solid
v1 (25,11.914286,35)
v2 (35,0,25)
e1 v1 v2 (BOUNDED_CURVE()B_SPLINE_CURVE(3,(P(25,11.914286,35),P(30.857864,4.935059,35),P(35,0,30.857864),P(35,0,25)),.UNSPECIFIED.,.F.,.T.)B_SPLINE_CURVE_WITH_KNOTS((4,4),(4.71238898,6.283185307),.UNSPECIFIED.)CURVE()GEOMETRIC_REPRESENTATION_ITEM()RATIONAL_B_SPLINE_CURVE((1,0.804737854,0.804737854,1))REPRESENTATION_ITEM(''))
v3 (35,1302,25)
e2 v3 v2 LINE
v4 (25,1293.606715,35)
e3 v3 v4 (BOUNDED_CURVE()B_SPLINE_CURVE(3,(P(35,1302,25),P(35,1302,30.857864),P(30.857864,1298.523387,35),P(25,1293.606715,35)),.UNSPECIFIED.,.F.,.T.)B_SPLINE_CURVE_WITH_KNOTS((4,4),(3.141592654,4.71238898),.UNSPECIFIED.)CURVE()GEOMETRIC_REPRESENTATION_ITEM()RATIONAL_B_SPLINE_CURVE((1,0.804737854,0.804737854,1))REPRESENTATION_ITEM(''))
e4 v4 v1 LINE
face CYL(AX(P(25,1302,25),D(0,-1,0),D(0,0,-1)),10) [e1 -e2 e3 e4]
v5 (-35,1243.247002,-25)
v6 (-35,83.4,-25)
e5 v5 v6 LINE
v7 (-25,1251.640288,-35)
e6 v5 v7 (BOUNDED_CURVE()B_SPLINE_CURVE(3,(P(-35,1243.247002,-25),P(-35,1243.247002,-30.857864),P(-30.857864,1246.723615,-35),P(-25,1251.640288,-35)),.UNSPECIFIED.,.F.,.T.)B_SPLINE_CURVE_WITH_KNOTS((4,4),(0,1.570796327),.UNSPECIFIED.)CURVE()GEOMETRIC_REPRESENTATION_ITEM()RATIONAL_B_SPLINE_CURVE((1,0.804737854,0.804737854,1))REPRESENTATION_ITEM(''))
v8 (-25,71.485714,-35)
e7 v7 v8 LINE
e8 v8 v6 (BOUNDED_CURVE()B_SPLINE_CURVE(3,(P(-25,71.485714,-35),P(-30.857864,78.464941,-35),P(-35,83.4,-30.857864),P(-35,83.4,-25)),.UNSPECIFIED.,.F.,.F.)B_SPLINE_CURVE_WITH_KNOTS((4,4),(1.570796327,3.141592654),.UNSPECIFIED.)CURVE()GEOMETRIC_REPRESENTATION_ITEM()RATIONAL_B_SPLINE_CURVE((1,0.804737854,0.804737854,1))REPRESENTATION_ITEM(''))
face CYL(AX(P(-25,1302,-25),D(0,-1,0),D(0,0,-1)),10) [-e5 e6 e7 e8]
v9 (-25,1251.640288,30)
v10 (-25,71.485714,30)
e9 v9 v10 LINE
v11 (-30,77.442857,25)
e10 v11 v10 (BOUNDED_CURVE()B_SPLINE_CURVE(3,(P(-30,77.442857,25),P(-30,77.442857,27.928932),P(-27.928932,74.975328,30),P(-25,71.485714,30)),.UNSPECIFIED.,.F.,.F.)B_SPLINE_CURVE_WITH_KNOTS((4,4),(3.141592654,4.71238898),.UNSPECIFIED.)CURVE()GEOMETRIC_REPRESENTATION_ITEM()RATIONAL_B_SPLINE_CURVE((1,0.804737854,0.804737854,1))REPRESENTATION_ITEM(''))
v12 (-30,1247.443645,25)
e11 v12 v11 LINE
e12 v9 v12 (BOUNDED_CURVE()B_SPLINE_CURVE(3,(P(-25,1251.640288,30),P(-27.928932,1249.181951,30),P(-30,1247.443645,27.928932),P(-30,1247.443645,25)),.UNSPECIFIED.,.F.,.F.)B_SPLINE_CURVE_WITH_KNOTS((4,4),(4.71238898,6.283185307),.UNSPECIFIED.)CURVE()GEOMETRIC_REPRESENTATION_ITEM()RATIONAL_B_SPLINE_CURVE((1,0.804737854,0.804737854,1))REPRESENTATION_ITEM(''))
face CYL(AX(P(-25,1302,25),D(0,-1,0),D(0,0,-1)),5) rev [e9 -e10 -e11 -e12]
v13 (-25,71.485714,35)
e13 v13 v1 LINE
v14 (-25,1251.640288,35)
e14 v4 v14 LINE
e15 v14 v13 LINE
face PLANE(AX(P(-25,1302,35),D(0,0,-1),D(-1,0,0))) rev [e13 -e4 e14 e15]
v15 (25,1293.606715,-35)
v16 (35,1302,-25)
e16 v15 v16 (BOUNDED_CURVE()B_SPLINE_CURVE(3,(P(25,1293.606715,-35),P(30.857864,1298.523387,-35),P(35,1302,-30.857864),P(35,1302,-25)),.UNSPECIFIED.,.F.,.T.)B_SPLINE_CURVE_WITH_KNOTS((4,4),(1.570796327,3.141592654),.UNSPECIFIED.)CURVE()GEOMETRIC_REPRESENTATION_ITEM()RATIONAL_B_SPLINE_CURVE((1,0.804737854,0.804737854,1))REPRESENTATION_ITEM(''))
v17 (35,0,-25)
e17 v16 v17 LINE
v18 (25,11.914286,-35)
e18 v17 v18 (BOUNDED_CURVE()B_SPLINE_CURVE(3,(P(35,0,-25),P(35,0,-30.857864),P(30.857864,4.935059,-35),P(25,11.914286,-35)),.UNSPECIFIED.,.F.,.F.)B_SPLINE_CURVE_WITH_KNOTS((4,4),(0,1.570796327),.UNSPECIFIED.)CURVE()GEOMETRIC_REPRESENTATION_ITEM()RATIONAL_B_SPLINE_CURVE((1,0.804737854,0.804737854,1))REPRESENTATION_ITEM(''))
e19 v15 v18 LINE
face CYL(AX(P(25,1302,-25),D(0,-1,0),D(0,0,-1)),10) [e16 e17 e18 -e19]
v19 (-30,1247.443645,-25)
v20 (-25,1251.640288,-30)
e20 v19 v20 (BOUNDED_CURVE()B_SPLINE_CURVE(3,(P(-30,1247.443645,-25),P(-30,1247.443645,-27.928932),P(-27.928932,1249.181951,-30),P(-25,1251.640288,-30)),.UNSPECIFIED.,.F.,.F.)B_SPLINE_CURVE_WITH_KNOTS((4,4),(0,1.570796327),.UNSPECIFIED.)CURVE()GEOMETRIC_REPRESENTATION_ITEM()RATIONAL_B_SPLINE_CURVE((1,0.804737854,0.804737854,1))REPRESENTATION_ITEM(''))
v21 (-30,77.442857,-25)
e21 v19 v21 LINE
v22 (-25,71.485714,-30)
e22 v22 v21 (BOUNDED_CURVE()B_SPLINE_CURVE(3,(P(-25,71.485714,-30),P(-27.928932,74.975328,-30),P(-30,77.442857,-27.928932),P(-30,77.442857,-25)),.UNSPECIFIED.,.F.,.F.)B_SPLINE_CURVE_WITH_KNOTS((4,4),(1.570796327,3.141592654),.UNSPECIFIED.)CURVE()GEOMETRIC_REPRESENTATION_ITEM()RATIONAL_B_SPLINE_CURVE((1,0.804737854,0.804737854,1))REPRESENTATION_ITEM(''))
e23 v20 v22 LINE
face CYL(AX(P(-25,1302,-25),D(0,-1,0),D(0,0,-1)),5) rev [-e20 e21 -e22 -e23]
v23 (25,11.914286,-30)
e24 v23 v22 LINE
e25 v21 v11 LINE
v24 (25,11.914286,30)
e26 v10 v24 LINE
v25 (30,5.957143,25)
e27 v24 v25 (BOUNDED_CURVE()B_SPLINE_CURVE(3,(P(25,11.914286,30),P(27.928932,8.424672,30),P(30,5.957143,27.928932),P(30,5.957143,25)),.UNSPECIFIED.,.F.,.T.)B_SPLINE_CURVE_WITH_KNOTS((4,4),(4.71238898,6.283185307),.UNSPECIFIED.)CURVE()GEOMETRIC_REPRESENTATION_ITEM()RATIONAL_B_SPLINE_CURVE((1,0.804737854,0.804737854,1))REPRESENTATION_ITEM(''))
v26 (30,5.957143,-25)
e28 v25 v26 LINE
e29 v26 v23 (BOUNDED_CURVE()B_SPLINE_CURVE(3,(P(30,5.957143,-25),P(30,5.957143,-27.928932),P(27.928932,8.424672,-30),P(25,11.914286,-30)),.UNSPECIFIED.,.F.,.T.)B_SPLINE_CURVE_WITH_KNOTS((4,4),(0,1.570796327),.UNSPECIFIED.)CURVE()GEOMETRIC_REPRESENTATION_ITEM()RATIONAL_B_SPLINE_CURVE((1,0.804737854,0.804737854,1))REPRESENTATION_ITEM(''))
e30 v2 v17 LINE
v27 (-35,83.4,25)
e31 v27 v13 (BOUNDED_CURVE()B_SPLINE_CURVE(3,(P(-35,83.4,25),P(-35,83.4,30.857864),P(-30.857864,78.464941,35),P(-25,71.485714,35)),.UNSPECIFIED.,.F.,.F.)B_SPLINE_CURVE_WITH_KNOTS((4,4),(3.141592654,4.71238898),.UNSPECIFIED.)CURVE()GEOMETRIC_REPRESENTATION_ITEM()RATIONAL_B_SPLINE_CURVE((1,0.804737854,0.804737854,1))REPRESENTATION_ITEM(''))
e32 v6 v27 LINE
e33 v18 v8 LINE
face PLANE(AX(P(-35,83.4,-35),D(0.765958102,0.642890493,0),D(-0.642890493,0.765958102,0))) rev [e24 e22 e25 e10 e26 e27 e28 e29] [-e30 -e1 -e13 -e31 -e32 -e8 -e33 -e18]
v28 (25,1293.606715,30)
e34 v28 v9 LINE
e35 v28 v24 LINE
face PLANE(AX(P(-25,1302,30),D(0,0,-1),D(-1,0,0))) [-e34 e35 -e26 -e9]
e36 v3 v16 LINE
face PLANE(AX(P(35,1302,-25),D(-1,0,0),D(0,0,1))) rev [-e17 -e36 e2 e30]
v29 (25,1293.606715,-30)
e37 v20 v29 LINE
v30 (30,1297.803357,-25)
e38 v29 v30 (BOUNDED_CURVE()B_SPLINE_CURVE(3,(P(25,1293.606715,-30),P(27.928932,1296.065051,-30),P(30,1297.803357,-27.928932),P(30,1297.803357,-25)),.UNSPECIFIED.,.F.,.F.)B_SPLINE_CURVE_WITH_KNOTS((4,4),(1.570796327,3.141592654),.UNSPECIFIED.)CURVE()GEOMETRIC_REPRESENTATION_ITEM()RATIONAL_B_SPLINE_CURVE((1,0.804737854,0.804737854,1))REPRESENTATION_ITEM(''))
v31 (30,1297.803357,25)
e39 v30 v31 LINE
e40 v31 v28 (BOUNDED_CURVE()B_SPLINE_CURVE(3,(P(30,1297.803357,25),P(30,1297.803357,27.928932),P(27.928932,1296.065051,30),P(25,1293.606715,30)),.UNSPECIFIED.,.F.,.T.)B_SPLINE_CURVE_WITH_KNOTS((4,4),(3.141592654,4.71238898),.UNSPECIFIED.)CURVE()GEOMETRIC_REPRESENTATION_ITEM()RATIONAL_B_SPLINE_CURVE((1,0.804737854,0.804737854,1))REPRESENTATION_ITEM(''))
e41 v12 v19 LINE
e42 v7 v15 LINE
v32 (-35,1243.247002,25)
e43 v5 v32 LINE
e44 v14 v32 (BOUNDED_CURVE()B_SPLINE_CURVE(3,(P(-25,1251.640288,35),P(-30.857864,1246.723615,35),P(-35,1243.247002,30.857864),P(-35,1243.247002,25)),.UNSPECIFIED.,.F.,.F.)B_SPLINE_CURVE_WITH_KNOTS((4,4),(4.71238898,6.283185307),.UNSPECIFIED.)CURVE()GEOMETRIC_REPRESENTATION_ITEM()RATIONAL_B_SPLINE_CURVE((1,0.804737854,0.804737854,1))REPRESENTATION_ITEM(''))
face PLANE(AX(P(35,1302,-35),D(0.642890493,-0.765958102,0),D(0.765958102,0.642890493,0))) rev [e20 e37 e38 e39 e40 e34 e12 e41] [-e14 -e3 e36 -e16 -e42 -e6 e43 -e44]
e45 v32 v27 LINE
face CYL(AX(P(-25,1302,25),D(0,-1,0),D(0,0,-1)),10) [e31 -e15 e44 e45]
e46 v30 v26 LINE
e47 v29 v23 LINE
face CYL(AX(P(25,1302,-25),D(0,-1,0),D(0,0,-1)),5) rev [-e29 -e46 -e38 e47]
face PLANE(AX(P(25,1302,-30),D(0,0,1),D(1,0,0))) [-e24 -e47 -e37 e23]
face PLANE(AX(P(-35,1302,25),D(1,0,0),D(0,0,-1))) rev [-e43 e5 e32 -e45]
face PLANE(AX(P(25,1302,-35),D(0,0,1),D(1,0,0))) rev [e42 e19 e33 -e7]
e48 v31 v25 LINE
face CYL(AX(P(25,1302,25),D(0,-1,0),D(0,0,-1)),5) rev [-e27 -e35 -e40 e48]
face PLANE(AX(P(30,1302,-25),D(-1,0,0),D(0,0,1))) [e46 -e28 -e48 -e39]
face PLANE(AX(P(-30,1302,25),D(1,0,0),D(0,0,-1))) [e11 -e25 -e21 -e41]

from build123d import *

# Parameters (mm, degrees)
F_19_WELDMEMBERFEAT_4_MORE_IN_5_FILES_DEPTH = 1302
CUT_EXTRUDE1_DEPTH                          = 1305.350029708
CUT_EXTRUDE1_DEPTH_BACK                     = 1305.350029708


with BuildPart() as part:
    # Sketch1 → 19 (WeldMemberFeat) (+4 more in 5 files) Cold-formed hollow square steel (GB/T 6728-2002) 70×70×5(1) (new body)
    with BuildSketch(Plane(origin=(0, 0, 0), x_dir=(-1, 0, 0), z_dir=(0, 1, 0))):
        with BuildLine():
            Line((-25, -35), (25, -35))
            ThreePointArc((25, -35), (32.071067812, -32.071067812), (35, -25))
            Line((35, -25), (35, 25))
            ThreePointArc((35, 25), (32.071067812, 32.071067812), (25, 35))
            Line((25, 35), (-25, 35))
            ThreePointArc((-25, 35), (-32.071067812, 32.071067812), (-35, 25))
            Line((-35, 25), (-35, -25))
            ThreePointArc((-35, -25), (-32.071067812, -32.071067812), (-25, -35))
        make_face()
        with BuildLine():
            Line((-25, -30), (25, -30))
            ThreePointArc((25, -30), (28.535533906, -28.535533906), (30, -25))
            Line((30, -25), (30, 25))
            ThreePointArc((30, 25), (28.535533906, 28.535533906), (25, 30))
            Line((25, 30), (-25, 30))
            ThreePointArc((-25, 30), (-28.535533906, 28.535533906), (-30, 25))
            Line((-30, 25), (-30, -25))
            ThreePointArc((-30, -25), (-28.535533906, -28.535533906), (-25, -30))
        make_face(mode=Mode.SUBTRACT)
    extrude(amount=F_19_WELDMEMBERFEAT_4_MORE_IN_5_FILES_DEPTH)

    # Sketch2 → Cut-Extrude1 (cut, two sides: drawn at the far end of the back side and taken through both)
    with BuildSketch(Plane.XY.offset(35).offset(-CUT_EXTRUDE1_DEPTH_BACK)):
        Polygon((35, 1302), (-35, 1243.247002398), (-35, 1302), align=None)
        Polygon((-35, 83.4), (35, 0), (-35, 0), align=None)
    extrude(amount=CUT_EXTRUDE1_DEPTH + CUT_EXTRUDE1_DEPTH_BACK, mode=Mode.SUBTRACT)


solid = part.part
